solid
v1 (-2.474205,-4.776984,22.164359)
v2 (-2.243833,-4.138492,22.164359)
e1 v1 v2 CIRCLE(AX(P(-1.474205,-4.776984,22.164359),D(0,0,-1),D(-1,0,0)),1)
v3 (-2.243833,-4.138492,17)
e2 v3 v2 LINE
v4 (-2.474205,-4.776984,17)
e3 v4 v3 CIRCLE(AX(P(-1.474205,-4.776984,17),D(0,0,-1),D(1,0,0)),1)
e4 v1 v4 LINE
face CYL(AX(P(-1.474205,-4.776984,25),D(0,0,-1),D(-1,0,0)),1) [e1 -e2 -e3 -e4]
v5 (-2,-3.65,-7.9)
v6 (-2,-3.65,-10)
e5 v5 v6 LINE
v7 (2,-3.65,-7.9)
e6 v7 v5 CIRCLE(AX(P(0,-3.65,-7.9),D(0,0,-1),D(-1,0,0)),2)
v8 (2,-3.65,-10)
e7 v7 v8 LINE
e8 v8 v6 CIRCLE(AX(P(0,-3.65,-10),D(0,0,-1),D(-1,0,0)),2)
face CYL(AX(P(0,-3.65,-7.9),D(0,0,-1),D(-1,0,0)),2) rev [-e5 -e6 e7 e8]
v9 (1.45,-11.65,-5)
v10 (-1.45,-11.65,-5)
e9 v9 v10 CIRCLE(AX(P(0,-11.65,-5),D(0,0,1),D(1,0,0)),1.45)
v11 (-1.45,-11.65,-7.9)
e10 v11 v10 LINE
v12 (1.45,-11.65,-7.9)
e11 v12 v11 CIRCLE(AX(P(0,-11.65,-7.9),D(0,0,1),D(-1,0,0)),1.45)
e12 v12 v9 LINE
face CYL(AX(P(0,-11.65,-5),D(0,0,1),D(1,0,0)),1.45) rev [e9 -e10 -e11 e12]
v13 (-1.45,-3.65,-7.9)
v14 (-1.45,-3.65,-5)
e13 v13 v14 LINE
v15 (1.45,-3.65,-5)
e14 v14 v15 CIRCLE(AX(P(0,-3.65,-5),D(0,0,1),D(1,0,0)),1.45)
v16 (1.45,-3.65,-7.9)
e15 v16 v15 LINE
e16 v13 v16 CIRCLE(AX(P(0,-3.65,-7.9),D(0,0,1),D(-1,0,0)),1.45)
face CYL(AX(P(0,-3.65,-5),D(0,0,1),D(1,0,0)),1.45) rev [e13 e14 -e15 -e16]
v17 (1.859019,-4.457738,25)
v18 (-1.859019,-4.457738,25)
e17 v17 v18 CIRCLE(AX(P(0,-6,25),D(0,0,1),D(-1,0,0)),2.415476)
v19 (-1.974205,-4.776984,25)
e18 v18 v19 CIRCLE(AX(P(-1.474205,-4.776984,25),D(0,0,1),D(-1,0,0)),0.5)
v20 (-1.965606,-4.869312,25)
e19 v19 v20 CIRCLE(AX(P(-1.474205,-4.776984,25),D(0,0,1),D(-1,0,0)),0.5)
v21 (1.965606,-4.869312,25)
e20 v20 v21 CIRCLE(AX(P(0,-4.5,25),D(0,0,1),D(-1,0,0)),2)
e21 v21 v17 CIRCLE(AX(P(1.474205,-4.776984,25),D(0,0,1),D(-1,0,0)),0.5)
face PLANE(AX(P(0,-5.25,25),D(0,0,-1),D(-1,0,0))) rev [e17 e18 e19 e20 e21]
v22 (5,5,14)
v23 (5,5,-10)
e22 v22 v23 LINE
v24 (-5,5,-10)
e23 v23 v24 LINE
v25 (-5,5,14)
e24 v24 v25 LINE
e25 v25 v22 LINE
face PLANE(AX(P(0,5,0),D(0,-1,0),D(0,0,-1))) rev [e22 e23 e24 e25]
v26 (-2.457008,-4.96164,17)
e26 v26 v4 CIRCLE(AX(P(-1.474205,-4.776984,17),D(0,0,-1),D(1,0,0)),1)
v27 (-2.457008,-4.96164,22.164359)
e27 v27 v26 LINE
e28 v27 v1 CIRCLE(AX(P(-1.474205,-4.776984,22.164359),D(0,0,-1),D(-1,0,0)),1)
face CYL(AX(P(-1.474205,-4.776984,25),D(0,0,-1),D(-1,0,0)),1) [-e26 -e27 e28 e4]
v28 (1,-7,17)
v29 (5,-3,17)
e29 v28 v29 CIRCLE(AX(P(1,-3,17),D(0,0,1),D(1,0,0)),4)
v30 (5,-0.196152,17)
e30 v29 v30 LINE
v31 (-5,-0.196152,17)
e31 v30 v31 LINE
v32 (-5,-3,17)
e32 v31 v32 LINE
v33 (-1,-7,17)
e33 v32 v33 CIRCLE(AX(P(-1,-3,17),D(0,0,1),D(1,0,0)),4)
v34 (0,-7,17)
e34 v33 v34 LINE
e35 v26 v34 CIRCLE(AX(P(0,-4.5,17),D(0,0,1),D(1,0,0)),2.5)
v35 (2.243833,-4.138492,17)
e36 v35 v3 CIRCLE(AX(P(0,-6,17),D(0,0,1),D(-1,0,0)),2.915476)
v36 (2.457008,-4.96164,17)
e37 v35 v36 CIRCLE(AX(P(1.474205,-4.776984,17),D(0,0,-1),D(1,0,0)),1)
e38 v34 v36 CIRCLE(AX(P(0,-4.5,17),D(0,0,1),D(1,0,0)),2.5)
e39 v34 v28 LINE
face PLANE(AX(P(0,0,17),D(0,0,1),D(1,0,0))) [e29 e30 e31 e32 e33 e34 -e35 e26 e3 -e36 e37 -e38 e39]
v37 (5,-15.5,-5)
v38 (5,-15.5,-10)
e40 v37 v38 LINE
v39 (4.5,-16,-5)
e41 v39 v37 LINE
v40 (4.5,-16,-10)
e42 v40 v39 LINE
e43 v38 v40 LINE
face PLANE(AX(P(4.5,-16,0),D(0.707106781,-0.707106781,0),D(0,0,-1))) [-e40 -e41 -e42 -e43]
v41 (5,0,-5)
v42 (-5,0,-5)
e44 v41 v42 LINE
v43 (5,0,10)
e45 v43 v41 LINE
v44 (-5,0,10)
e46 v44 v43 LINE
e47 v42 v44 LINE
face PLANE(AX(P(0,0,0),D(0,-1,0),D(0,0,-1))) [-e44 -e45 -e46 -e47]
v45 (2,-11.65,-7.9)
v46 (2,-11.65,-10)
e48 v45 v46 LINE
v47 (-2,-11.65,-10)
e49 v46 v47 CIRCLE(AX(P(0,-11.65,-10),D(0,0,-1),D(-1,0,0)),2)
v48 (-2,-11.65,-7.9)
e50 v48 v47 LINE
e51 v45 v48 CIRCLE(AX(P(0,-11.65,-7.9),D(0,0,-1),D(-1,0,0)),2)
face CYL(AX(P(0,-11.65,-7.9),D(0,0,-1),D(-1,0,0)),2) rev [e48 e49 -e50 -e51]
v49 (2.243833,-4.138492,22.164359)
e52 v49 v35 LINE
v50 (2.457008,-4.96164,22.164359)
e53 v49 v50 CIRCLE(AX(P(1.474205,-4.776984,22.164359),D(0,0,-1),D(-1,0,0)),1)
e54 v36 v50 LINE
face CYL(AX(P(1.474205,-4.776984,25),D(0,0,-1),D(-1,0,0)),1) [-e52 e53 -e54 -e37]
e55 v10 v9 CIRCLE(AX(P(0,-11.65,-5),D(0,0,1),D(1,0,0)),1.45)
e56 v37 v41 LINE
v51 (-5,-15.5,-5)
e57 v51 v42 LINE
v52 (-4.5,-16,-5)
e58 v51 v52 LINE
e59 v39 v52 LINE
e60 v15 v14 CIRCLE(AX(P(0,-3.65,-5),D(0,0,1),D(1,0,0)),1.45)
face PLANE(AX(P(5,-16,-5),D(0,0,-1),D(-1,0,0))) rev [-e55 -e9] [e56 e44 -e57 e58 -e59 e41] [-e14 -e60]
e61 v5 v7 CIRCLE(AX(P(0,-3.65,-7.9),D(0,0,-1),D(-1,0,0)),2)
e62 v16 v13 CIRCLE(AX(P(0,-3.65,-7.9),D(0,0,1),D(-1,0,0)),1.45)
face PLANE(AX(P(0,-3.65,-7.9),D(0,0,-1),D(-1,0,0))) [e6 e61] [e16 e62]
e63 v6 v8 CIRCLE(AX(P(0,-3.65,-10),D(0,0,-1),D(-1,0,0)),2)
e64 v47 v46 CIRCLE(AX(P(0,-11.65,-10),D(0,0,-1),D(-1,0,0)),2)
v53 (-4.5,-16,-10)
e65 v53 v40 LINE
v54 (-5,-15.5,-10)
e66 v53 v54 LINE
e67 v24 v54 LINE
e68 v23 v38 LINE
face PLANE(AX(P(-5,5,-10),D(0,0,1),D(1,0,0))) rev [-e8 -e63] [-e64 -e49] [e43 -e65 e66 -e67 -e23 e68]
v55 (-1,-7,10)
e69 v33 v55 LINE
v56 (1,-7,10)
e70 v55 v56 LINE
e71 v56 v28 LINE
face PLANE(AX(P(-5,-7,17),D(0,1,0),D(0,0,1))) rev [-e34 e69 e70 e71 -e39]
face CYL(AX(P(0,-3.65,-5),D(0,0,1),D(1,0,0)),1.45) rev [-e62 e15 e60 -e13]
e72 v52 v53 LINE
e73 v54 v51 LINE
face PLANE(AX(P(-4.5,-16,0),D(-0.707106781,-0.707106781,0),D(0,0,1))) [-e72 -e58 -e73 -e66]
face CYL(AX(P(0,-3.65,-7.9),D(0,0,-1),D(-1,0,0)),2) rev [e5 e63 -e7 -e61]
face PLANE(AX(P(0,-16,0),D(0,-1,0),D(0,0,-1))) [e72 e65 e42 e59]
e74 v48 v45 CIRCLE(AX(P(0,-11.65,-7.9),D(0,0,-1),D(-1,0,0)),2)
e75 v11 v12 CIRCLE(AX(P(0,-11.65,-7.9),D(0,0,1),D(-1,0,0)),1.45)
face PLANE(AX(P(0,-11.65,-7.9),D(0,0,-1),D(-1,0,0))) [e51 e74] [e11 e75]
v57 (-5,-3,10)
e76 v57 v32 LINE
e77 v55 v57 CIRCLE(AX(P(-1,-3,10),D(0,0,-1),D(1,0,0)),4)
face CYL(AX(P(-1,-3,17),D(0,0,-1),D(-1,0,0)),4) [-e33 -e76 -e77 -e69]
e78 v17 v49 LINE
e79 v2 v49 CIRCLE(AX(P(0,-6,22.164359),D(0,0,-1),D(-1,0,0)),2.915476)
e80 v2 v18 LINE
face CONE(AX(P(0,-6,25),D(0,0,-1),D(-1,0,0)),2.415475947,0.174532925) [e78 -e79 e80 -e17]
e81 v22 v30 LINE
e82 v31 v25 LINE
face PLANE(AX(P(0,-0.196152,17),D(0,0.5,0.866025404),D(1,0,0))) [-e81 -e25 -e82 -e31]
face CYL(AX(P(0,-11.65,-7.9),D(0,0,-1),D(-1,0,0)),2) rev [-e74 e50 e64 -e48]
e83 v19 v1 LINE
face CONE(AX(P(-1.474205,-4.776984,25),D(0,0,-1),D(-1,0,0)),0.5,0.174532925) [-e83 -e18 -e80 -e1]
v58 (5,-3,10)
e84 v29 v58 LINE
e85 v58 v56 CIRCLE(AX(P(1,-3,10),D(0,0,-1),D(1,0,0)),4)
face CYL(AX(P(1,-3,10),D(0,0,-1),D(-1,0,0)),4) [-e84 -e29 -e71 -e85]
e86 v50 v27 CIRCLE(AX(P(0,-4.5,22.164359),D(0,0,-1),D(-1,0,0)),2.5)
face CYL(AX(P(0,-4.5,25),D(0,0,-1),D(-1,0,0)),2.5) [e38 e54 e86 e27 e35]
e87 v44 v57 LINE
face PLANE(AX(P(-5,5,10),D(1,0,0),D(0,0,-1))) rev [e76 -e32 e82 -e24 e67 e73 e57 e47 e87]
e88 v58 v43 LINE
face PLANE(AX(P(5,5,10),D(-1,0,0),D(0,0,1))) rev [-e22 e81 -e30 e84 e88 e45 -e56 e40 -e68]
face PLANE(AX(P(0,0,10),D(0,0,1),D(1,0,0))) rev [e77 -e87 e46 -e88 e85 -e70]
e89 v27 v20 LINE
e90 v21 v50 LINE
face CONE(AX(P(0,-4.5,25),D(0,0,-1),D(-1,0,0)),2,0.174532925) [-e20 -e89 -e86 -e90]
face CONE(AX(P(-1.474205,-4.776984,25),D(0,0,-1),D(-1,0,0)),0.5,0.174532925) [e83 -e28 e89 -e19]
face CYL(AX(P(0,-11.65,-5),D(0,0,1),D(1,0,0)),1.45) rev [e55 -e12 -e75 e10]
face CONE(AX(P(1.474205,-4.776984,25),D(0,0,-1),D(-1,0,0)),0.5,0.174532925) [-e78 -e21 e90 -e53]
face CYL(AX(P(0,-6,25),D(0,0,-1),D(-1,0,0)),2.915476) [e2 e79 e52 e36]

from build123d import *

# Parameters (mm, degrees)
SKETCH1_W              = 10
SKETCH1_H              = 20
BOSS_EXTRUDE1_DEPTH    = 5
SKETCH2_W              = 10
SKETCH2_H              = 5
BOSS_EXTRUDE2_DEPTH    = 16
M2_5_CLEARANCE_HOLE1_D = 2.9
SKETCH6_W              = 10
SKETCH6_H              = 12
BOSS_EXTRUDE4_DEPTH    = 7
CHAMFER1_SIZE          = 3
CHAMFER1_SIZE2         = 5.196152423
FILLET1_R              = 4
CHAMFER2_SIZE          = 0.5
BOSS_EXTRUDE6_DEPTH    = 8
FILLET3_R              = 1
CHAMFER3_SIZE          = 0.5
CHAMFER3_SIZE2         = 2.83564091
SKETCH9_R              = 2
CUT_EXTRUDE1_DEPTH     = 2.1


with BuildPart() as part:
    # Sketch1 → Boss-Extrude1 (new body)
    with BuildSketch(Plane(origin=(0, 0, 0), x_dir=(1, 0, 0), z_dir=(0, 1, 0))):
        Rectangle(SKETCH1_W, SKETCH1_H)
    extrude(amount=BOSS_EXTRUDE1_DEPTH)

    # Sketch2 → Boss-Extrude2 (add)
    with BuildSketch(Plane(origin=(0, 0, 0), x_dir=(-1, 0, 0), z_dir=(0, -1, 0))):
        with Locations((0, 7.5)):
            Rectangle(SKETCH2_W, SKETCH2_H)
    extrude(amount=BOSS_EXTRUDE2_DEPTH)

    # M2.5 Clearance Hole1 (through all)
    with Locations(Plane.XY.offset(-5)):
        with Locations((0, -11.65), (0, -3.65)):
            Hole(M2_5_CLEARANCE_HOLE1_D / 2)

    # Sketch6 → Boss-Extrude4 (add)
    with BuildSketch(Plane.XY.offset(10)):
        with Locations((0, -1)):
            Rectangle(SKETCH6_W, SKETCH6_H)
    extrude(amount=BOSS_EXTRUDE4_DEPTH)

    # Chamfer1
    chamfer1_edges = [part.edges().sort_by_distance(p)[0] for p in [
        (0, 5, 17),
    ]]
    chamfer1_side = [part.faces().sort_by_distance(p)[0] for p in [
        (0, 5, 3.5),
    ]]
    chamfer(chamfer1_edges, length=CHAMFER1_SIZE, length2=CHAMFER1_SIZE2, reference=chamfer1_side[0])

    # Fillet1
    fillet1_edges = [part.edges().sort_by_distance(p)[0] for p in [
        (5, -7, 13.5),
        (-5, -7, 13.5),
    ]]
    fillet(fillet1_edges, radius=FILLET1_R)

    # Chamfer2
    chamfer2_edges = [part.edges().sort_by_distance(p)[0] for p in [
        (5, -16, -7.5),
        (-5, -16, -7.5),
    ]]
    chamfer(chamfer2_edges, length=CHAMFER2_SIZE)

    # Sketch8 → Boss-Extrude6 (add)
    with BuildSketch(Plane.XY.offset(17)):
        with BuildLine():
            ThreePointArc((-2.5, -4.5), (0, -7), (2.5, -4.5))
            ThreePointArc((2.5, -4.5), (0, -3.084524053), (-2.5, -4.5))
        make_face()
    extrude(amount=BOSS_EXTRUDE6_DEPTH)

    # Fillet3
    fillet3_edges = [part.edges().sort_by_distance(p)[0] for p in [
        (2.5, -4.5, 21),
        (-2.5, -4.5, 21),
    ]]
    fillet(fillet3_edges, radius=FILLET3_R)

    # Chamfer3
    chamfer3_edges = [part.edges().sort_by_distance(p)[0] for p in [
        (0, -3.084524053, 25),
        (0, -7, 25),
        (-2.442268543, -4.526279661, 25),
        (2.442268543, -4.526279661, 25),
    ]]
    chamfer3_side = [part.faces().sort_by_distance(p)[0] for p in [
        (0, -5.00792315, 25),
    ]]
    chamfer(chamfer3_edges, length=CHAMFER3_SIZE, length2=CHAMFER3_SIZE2, reference=chamfer3_side[0])

    # Sketch9 → Cut-Extrude1 (cut)
    with BuildSketch(Plane(origin=(0, 0, -10), x_dir=(-1, 0, 0), z_dir=(0, 0, -1))):
        with Locations((0, -3.65)):
            Circle(SKETCH9_R)
        with Locations((0, -11.65)):
            Circle(SKETCH9_R)
    extrude(amount=-CUT_EXTRUDE1_DEPTH, mode=Mode.SUBTRACT)


solid = part.part
